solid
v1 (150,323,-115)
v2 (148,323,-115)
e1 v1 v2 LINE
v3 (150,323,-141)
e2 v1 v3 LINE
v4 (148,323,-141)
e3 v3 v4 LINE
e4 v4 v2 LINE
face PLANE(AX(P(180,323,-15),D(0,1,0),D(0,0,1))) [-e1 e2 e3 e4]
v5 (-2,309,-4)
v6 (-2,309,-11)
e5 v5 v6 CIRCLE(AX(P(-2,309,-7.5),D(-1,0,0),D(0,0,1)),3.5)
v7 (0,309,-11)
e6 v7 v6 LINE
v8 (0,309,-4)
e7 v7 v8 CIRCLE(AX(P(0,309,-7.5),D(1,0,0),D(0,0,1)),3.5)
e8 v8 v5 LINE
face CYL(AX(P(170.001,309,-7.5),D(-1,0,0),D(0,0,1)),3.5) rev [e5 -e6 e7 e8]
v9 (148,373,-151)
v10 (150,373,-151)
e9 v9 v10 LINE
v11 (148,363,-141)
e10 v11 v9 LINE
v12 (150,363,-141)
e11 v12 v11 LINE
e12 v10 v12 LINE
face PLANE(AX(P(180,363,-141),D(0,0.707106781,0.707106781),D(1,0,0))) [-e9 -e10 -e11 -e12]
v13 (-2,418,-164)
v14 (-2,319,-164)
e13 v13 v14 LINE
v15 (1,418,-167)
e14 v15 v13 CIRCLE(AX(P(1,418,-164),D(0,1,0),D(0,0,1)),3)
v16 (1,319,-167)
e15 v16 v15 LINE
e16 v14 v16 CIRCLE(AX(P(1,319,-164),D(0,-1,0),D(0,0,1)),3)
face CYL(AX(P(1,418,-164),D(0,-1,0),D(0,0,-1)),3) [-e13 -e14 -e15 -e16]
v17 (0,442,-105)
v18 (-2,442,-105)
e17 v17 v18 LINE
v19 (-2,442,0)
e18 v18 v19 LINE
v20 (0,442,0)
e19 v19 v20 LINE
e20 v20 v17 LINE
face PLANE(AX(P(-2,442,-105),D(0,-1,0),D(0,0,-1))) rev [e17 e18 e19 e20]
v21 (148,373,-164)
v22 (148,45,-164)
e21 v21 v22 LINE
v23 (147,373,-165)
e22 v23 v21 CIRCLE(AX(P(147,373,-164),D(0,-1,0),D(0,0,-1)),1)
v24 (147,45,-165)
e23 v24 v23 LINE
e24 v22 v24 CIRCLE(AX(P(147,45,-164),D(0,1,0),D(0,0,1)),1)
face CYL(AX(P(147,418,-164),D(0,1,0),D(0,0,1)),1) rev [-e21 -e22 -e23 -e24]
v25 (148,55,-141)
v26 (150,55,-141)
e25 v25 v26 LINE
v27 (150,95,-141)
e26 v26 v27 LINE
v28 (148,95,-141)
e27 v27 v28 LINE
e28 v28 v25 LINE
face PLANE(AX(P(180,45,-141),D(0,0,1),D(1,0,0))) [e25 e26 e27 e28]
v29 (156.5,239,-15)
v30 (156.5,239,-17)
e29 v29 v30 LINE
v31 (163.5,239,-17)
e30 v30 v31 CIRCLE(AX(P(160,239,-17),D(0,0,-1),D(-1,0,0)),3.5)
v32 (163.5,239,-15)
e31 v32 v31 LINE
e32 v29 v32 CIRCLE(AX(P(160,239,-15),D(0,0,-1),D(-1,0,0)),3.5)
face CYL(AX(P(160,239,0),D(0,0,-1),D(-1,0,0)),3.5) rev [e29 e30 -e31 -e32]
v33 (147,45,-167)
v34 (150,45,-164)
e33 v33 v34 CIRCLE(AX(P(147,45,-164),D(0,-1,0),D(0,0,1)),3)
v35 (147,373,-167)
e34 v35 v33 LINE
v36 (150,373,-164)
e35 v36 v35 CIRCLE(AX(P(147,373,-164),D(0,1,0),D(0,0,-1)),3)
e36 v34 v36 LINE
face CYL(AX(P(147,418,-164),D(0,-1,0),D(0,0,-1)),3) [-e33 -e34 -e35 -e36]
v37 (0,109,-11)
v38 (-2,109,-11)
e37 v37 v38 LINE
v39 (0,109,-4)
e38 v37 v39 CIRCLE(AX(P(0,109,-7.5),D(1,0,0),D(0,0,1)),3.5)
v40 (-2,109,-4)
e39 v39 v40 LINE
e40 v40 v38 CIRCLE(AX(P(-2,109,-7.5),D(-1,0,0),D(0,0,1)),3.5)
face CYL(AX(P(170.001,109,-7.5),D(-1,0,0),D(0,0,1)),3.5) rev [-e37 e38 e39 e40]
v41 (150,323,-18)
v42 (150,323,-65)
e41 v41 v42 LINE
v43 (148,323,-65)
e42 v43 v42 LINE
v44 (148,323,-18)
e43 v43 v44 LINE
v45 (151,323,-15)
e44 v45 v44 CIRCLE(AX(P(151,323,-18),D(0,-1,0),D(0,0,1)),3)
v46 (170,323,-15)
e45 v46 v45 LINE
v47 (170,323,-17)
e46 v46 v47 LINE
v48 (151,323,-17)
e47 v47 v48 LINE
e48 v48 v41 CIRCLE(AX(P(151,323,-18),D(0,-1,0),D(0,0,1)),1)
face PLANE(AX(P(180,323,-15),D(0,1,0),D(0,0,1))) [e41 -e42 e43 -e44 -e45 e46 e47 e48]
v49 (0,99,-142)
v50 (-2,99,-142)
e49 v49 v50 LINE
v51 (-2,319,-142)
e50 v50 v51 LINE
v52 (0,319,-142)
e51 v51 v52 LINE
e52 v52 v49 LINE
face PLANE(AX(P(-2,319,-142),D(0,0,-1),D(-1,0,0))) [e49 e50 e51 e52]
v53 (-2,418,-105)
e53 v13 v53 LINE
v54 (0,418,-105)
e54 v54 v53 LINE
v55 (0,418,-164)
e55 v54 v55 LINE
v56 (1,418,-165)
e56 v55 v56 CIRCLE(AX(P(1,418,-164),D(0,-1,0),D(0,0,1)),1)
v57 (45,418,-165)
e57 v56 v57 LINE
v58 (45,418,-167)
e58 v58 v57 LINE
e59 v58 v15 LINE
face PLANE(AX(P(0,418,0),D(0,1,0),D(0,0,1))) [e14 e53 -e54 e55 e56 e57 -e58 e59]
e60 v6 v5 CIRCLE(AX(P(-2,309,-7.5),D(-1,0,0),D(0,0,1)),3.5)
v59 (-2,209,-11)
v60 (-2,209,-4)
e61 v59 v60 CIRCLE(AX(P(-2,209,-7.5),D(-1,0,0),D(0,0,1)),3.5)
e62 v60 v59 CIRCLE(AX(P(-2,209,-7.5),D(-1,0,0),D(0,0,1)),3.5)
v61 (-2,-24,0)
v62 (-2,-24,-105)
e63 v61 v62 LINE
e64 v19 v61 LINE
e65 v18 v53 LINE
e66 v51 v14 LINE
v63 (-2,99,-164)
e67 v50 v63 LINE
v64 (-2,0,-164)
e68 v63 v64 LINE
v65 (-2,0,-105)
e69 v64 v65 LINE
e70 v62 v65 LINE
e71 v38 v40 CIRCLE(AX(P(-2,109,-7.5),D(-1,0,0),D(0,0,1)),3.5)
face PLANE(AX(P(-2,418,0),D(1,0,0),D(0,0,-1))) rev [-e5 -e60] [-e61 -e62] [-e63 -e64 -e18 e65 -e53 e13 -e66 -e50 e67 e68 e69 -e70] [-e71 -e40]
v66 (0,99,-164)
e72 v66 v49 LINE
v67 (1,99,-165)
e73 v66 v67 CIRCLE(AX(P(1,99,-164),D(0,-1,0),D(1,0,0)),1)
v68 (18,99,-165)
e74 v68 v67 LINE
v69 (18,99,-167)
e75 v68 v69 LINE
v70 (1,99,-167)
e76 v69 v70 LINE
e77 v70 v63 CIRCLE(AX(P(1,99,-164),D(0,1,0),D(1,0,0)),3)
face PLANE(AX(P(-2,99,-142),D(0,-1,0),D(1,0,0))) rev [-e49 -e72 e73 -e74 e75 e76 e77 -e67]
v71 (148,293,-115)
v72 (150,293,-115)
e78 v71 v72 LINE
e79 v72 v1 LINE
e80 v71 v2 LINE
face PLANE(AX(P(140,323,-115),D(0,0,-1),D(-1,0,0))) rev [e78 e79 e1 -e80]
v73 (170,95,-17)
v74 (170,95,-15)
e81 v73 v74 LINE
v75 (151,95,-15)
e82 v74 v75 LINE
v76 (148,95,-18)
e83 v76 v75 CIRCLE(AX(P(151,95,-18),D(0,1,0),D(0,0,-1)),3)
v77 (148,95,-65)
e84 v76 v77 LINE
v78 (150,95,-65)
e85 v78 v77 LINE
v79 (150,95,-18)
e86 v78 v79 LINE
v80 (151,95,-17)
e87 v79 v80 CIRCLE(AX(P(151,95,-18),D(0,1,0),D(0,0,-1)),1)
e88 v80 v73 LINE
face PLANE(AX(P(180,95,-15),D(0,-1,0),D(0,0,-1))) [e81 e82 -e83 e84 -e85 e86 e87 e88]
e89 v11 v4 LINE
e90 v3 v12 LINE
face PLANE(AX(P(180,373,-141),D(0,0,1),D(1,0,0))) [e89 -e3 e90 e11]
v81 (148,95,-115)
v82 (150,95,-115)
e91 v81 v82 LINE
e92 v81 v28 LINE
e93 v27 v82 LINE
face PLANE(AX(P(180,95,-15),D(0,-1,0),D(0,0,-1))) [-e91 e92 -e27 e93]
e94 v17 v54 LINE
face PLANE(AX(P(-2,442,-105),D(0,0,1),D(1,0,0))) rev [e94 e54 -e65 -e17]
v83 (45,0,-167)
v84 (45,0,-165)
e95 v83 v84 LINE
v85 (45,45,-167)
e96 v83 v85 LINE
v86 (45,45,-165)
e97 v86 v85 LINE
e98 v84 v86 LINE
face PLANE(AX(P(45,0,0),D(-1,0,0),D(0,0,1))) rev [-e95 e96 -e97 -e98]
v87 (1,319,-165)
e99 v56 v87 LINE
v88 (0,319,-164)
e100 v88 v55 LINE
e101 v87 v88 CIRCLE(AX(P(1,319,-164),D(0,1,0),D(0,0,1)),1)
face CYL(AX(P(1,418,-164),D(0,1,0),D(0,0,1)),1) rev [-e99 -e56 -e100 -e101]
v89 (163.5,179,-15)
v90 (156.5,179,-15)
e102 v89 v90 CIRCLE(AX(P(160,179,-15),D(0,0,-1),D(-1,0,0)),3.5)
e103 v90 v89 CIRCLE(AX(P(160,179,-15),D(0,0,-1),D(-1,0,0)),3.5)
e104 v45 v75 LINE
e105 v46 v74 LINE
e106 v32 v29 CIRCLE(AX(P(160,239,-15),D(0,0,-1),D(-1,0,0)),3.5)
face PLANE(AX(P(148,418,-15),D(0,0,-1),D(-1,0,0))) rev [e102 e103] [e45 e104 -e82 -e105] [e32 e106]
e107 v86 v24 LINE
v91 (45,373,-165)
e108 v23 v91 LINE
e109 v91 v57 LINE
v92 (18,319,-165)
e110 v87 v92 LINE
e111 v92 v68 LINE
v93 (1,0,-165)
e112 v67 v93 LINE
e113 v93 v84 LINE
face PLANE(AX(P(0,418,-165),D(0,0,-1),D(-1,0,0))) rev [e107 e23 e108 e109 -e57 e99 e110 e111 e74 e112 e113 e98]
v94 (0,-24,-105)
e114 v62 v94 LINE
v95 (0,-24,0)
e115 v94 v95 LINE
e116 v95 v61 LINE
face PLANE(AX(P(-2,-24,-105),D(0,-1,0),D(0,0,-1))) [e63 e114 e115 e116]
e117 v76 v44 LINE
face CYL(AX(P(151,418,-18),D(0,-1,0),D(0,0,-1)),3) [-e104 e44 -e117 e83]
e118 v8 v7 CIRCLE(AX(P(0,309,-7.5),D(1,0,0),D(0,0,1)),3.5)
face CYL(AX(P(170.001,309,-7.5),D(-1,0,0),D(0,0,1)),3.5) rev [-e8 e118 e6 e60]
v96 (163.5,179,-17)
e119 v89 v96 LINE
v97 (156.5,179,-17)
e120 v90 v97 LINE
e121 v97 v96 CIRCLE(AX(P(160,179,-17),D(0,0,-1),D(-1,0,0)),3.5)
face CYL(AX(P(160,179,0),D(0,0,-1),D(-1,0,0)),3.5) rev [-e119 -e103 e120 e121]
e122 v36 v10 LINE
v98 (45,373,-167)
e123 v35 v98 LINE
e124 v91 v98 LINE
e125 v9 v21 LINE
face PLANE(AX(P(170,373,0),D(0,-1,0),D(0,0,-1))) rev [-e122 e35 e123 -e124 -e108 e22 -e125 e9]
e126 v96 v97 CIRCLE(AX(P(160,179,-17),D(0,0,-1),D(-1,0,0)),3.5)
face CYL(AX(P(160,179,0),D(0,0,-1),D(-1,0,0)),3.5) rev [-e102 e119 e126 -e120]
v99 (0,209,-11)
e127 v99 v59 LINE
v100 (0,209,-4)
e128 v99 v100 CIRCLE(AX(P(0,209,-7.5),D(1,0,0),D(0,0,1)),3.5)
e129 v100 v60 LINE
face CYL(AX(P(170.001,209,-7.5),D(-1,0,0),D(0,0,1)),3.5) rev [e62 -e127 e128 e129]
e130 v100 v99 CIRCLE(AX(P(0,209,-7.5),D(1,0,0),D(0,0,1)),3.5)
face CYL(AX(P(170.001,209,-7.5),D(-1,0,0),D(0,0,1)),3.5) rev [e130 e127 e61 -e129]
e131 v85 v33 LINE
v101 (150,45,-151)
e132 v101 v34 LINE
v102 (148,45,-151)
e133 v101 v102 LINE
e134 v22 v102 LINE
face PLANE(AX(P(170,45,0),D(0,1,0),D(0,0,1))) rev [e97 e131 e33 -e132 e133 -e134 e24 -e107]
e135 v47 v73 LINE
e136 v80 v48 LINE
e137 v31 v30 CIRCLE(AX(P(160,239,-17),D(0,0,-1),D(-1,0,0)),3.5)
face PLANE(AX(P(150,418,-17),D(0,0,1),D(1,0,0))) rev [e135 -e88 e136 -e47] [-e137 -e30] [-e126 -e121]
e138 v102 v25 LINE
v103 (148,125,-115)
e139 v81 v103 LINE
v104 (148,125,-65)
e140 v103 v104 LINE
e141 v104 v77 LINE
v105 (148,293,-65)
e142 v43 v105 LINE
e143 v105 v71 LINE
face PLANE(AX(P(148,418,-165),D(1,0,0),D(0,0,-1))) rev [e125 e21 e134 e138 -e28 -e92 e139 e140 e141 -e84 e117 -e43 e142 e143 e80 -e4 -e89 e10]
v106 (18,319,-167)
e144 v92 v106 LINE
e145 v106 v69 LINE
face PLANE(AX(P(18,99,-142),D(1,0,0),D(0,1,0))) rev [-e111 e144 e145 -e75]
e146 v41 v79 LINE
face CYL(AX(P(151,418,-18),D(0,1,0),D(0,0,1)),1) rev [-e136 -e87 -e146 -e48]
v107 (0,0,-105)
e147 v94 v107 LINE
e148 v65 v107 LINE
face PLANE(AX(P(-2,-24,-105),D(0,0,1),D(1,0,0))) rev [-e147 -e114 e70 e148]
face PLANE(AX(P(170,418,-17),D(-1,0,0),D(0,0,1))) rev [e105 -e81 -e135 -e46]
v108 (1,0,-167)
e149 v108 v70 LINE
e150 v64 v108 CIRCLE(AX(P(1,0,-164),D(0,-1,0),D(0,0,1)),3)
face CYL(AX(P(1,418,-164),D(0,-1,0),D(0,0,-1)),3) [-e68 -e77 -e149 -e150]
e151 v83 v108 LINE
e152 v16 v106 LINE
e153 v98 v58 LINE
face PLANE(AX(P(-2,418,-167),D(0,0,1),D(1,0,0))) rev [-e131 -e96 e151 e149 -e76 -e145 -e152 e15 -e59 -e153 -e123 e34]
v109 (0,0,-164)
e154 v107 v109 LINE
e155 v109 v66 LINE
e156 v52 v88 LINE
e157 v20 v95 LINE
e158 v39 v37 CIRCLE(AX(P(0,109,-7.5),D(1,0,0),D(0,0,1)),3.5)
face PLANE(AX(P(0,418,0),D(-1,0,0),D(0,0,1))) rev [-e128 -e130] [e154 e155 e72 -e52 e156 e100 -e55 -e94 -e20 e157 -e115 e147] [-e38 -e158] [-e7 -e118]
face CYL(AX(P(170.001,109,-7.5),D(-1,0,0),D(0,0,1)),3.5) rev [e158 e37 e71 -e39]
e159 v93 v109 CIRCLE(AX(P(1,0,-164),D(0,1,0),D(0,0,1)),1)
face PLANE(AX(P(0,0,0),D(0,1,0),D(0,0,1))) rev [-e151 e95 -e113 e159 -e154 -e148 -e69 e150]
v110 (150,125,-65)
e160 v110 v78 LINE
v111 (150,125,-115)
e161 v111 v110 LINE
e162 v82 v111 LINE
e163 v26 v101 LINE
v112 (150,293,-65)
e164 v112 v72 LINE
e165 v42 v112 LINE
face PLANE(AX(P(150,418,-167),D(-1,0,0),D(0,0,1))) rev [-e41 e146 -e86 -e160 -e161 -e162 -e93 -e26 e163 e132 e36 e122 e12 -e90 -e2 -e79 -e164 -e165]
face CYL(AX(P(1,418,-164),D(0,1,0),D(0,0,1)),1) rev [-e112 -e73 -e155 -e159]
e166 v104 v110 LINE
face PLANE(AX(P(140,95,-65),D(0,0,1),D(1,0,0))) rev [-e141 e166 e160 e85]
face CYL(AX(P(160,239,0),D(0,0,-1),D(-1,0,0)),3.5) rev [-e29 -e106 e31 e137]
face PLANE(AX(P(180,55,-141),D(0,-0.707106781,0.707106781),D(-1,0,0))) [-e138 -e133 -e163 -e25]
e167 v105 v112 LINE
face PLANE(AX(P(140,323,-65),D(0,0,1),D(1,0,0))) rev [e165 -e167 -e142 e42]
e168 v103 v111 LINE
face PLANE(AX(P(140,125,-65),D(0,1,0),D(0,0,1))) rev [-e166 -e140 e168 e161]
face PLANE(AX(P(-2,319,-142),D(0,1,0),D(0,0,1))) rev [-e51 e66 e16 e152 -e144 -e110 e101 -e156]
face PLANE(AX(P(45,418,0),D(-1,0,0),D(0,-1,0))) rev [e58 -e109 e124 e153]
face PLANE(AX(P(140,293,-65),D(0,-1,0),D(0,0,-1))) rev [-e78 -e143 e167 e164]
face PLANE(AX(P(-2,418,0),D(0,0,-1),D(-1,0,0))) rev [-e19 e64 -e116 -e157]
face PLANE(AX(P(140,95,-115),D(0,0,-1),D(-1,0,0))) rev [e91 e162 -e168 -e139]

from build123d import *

# Parameters (mm, degrees)
BOSS_EXTRUDE1_DEPTH     = 418
SKETCH2_W               = 20
SKETCH2_H               = 220
CUT_EXTRUDE1_DEPTH      = 25
SKETCH3_W               = 125
SKETCH3_H               = 45
CUT_EXTRUDE2_DEPTH      = 482.157978215
FILLET1_R               = 3
FILLET2_R               = 1
SKETCH5_R               = 3.5
CUT_EXTRUDE4_DEPTH      = 476.524973056
CUT_EXTRUDE5_REACH      = 483.868
SKETCH6_R               = 3.5
SKETCH8_W               = 2
SKETCH8_H               = 105
BOSS_EXTRUDE2_DEPTH     = 24
SKETCH9_W               = 2
SKETCH9_H               = 105
BOSS_EXTRUDE3_DEPTH     = 24
CUT_EXTRUDE6_DEPTH      = 30
CUT_EXTRUDE6_DEPTH_BACK = 10
SKETCH10_W              = 126
SKETCH10_H              = 50
CHAMFER1_SIZE           = 10
SKETCH11_W              = 50
SKETCH11_H              = 30
CUT_EXTRUDE7_DEPTH      = 10


with BuildPart() as part:
    # Sketch1 → Boss-Extrude1 (new body)
    with BuildSketch(Plane(origin=(0, 0, 0), x_dir=(1, 0, 0), z_dir=(0, 1, 0))):
        Polygon((0, 0), (0, 165), (148, 165), (148, 15), (170, 15), (170, 17), (150, 17), (150, 167), (-2, 167), (-2, 0), align=None)
    extrude(amount=BOSS_EXTRUDE1_DEPTH)

    # Sketch2 → Cut-Extrude1 (cut)
    with BuildSketch(Plane(origin=(0, 0, -167), x_dir=(-1, 0, 0), z_dir=(0, 0, -1))):
        with Locations((-8, 209)):
            Rectangle(SKETCH2_W, SKETCH2_H)
    extrude(amount=-CUT_EXTRUDE1_DEPTH, mode=Mode.SUBTRACT)

    # Sketch3 → Cut-Extrude2 (cut, through all)
    with BuildSketch(Plane(origin=(0, 0, -167), x_dir=(-1, 0, 0), z_dir=(0, 0, -1))):
        with Locations((-107.5, 395.5)):
            Rectangle(SKETCH3_W, SKETCH3_H)
        with Locations((-107.5, 22.5)):
            Rectangle(SKETCH3_W, SKETCH3_H)
    extrude(amount=-CUT_EXTRUDE2_DEPTH, mode=Mode.SUBTRACT)

    # Fillet1
    fillet1_edges = [part.edges().sort_by_distance(p)[0] for p in [
        (-2, 368.5, -167),
        (-2, 49.5, -167),
        (150, 209, -167),
        (148, 209, -15),
    ]]
    fillet(fillet1_edges, radius=FILLET1_R)

    # Fillet2
    fillet2_edges = [part.edges().sort_by_distance(p)[0] for p in [
        (0, 368.5, -165),
        (0, 49.5, -165),
        (150, 209, -17),
        (148, 209, -165),
    ]]
    fillet(fillet2_edges, radius=FILLET2_R)

    # Sketch5 → Cut-Extrude4 (cut, through all)
    with BuildSketch(Plane(origin=(0, 0, -17), x_dir=(-1, 0, 0), z_dir=(0, 0, -1))):
        with Locations((-160, 239)):
            Circle(SKETCH5_R)
        with Locations((-160, 179)):
            Circle(SKETCH5_R)
    extrude(amount=-CUT_EXTRUDE4_DEPTH, mode=Mode.SUBTRACT)

    # Sketch6 → Cut-Extrude5 (cut, up to next)
    with BuildSketch(Plane.ZY.offset(2), mode=Mode.PRIVATE) as cut_extrude5_sk1:
        with Locations((-7.5, 309)):
            Circle(SKETCH6_R)
    cut_extrude5_tool1 = extrude(cut_extrude5_sk1.sketch, amount=-CUT_EXTRUDE5_REACH, mode=Mode.PRIVATE) & part.part
    # Sketch6 → Cut-Extrude5 (cut, up to next)
    with BuildSketch(Plane.ZY.offset(2), mode=Mode.PRIVATE) as cut_extrude5_sk2:
        with Locations((-7.5, 209)):
            Circle(SKETCH6_R)
    cut_extrude5_tool2 = extrude(cut_extrude5_sk2.sketch, amount=-CUT_EXTRUDE5_REACH, mode=Mode.PRIVATE) & part.part
    # Sketch6 → Cut-Extrude5 (cut, up to next)
    with BuildSketch(Plane.ZY.offset(2), mode=Mode.PRIVATE) as cut_extrude5_sk3:
        with Locations((-7.5, 109)):
            Circle(SKETCH6_R)
    cut_extrude5_tool3 = extrude(cut_extrude5_sk3.sketch, amount=-CUT_EXTRUDE5_REACH, mode=Mode.PRIVATE) & part.part
    add(cut_extrude5_tool1.solids().sort_by_distance((-2, 309, -7.5))[0], mode=Mode.SUBTRACT)
    add(cut_extrude5_tool2.solids().sort_by_distance((-2, 209, -7.5))[0], mode=Mode.SUBTRACT)
    add(cut_extrude5_tool3.solids().sort_by_distance((-2, 109, -7.5))[0], mode=Mode.SUBTRACT)

    # Sketch8 → Boss-Extrude2 (add)
    with BuildSketch(Plane.XZ):
        with Locations((-1, -52.5)):
            Rectangle(SKETCH8_W, SKETCH8_H)
    extrude(amount=BOSS_EXTRUDE2_DEPTH)

    # Sketch9 → Boss-Extrude3 (add)
    with BuildSketch(Plane(origin=(0, 418, 0), x_dir=(1, 0, 0), z_dir=(0, 1, 0))):
        with Locations((-1, 52.5)):
            Rectangle(SKETCH9_W, SKETCH9_H)
    extrude(amount=BOSS_EXTRUDE3_DEPTH)

    # Sketch10 → Cut-Extrude6 (cut, two sides: drawn at the far end of the back side and taken through both)
    with BuildSketch(Plane(origin=(150, 0, 0), x_dir=(0, 0, -1), z_dir=(1, 0, 0)).offset(-CUT_EXTRUDE6_DEPTH_BACK)):
        with Locations((78, 348)):
            Rectangle(SKETCH10_W, SKETCH10_H)
        with Locations((78, 70)):
            Rectangle(SKETCH10_W, SKETCH10_H)
    extrude(amount=CUT_EXTRUDE6_DEPTH + CUT_EXTRUDE6_DEPTH_BACK, mode=Mode.SUBTRACT)

    # Chamfer1
    chamfer1_edges = [part.edges().sort_by_distance(p)[0] for p in [
        (149, 373, -141),
        (149, 45, -141),
    ]]
    chamfer(chamfer1_edges, length=CHAMFER1_SIZE)

    # Sketch11 → Cut-Extrude7 (cut)
    with BuildSketch(Plane(origin=(150, 0, 0), x_dir=(0, 0, -1), z_dir=(1, 0, 0))):
        with Locations((90, 110)):
            Rectangle(SKETCH11_W, SKETCH11_H)
        with Locations((90, 308)):
            Rectangle(SKETCH11_W, SKETCH11_H)
    extrude(amount=-CUT_EXTRUDE7_DEPTH, mode=Mode.SUBTRACT)


solid = part.part
